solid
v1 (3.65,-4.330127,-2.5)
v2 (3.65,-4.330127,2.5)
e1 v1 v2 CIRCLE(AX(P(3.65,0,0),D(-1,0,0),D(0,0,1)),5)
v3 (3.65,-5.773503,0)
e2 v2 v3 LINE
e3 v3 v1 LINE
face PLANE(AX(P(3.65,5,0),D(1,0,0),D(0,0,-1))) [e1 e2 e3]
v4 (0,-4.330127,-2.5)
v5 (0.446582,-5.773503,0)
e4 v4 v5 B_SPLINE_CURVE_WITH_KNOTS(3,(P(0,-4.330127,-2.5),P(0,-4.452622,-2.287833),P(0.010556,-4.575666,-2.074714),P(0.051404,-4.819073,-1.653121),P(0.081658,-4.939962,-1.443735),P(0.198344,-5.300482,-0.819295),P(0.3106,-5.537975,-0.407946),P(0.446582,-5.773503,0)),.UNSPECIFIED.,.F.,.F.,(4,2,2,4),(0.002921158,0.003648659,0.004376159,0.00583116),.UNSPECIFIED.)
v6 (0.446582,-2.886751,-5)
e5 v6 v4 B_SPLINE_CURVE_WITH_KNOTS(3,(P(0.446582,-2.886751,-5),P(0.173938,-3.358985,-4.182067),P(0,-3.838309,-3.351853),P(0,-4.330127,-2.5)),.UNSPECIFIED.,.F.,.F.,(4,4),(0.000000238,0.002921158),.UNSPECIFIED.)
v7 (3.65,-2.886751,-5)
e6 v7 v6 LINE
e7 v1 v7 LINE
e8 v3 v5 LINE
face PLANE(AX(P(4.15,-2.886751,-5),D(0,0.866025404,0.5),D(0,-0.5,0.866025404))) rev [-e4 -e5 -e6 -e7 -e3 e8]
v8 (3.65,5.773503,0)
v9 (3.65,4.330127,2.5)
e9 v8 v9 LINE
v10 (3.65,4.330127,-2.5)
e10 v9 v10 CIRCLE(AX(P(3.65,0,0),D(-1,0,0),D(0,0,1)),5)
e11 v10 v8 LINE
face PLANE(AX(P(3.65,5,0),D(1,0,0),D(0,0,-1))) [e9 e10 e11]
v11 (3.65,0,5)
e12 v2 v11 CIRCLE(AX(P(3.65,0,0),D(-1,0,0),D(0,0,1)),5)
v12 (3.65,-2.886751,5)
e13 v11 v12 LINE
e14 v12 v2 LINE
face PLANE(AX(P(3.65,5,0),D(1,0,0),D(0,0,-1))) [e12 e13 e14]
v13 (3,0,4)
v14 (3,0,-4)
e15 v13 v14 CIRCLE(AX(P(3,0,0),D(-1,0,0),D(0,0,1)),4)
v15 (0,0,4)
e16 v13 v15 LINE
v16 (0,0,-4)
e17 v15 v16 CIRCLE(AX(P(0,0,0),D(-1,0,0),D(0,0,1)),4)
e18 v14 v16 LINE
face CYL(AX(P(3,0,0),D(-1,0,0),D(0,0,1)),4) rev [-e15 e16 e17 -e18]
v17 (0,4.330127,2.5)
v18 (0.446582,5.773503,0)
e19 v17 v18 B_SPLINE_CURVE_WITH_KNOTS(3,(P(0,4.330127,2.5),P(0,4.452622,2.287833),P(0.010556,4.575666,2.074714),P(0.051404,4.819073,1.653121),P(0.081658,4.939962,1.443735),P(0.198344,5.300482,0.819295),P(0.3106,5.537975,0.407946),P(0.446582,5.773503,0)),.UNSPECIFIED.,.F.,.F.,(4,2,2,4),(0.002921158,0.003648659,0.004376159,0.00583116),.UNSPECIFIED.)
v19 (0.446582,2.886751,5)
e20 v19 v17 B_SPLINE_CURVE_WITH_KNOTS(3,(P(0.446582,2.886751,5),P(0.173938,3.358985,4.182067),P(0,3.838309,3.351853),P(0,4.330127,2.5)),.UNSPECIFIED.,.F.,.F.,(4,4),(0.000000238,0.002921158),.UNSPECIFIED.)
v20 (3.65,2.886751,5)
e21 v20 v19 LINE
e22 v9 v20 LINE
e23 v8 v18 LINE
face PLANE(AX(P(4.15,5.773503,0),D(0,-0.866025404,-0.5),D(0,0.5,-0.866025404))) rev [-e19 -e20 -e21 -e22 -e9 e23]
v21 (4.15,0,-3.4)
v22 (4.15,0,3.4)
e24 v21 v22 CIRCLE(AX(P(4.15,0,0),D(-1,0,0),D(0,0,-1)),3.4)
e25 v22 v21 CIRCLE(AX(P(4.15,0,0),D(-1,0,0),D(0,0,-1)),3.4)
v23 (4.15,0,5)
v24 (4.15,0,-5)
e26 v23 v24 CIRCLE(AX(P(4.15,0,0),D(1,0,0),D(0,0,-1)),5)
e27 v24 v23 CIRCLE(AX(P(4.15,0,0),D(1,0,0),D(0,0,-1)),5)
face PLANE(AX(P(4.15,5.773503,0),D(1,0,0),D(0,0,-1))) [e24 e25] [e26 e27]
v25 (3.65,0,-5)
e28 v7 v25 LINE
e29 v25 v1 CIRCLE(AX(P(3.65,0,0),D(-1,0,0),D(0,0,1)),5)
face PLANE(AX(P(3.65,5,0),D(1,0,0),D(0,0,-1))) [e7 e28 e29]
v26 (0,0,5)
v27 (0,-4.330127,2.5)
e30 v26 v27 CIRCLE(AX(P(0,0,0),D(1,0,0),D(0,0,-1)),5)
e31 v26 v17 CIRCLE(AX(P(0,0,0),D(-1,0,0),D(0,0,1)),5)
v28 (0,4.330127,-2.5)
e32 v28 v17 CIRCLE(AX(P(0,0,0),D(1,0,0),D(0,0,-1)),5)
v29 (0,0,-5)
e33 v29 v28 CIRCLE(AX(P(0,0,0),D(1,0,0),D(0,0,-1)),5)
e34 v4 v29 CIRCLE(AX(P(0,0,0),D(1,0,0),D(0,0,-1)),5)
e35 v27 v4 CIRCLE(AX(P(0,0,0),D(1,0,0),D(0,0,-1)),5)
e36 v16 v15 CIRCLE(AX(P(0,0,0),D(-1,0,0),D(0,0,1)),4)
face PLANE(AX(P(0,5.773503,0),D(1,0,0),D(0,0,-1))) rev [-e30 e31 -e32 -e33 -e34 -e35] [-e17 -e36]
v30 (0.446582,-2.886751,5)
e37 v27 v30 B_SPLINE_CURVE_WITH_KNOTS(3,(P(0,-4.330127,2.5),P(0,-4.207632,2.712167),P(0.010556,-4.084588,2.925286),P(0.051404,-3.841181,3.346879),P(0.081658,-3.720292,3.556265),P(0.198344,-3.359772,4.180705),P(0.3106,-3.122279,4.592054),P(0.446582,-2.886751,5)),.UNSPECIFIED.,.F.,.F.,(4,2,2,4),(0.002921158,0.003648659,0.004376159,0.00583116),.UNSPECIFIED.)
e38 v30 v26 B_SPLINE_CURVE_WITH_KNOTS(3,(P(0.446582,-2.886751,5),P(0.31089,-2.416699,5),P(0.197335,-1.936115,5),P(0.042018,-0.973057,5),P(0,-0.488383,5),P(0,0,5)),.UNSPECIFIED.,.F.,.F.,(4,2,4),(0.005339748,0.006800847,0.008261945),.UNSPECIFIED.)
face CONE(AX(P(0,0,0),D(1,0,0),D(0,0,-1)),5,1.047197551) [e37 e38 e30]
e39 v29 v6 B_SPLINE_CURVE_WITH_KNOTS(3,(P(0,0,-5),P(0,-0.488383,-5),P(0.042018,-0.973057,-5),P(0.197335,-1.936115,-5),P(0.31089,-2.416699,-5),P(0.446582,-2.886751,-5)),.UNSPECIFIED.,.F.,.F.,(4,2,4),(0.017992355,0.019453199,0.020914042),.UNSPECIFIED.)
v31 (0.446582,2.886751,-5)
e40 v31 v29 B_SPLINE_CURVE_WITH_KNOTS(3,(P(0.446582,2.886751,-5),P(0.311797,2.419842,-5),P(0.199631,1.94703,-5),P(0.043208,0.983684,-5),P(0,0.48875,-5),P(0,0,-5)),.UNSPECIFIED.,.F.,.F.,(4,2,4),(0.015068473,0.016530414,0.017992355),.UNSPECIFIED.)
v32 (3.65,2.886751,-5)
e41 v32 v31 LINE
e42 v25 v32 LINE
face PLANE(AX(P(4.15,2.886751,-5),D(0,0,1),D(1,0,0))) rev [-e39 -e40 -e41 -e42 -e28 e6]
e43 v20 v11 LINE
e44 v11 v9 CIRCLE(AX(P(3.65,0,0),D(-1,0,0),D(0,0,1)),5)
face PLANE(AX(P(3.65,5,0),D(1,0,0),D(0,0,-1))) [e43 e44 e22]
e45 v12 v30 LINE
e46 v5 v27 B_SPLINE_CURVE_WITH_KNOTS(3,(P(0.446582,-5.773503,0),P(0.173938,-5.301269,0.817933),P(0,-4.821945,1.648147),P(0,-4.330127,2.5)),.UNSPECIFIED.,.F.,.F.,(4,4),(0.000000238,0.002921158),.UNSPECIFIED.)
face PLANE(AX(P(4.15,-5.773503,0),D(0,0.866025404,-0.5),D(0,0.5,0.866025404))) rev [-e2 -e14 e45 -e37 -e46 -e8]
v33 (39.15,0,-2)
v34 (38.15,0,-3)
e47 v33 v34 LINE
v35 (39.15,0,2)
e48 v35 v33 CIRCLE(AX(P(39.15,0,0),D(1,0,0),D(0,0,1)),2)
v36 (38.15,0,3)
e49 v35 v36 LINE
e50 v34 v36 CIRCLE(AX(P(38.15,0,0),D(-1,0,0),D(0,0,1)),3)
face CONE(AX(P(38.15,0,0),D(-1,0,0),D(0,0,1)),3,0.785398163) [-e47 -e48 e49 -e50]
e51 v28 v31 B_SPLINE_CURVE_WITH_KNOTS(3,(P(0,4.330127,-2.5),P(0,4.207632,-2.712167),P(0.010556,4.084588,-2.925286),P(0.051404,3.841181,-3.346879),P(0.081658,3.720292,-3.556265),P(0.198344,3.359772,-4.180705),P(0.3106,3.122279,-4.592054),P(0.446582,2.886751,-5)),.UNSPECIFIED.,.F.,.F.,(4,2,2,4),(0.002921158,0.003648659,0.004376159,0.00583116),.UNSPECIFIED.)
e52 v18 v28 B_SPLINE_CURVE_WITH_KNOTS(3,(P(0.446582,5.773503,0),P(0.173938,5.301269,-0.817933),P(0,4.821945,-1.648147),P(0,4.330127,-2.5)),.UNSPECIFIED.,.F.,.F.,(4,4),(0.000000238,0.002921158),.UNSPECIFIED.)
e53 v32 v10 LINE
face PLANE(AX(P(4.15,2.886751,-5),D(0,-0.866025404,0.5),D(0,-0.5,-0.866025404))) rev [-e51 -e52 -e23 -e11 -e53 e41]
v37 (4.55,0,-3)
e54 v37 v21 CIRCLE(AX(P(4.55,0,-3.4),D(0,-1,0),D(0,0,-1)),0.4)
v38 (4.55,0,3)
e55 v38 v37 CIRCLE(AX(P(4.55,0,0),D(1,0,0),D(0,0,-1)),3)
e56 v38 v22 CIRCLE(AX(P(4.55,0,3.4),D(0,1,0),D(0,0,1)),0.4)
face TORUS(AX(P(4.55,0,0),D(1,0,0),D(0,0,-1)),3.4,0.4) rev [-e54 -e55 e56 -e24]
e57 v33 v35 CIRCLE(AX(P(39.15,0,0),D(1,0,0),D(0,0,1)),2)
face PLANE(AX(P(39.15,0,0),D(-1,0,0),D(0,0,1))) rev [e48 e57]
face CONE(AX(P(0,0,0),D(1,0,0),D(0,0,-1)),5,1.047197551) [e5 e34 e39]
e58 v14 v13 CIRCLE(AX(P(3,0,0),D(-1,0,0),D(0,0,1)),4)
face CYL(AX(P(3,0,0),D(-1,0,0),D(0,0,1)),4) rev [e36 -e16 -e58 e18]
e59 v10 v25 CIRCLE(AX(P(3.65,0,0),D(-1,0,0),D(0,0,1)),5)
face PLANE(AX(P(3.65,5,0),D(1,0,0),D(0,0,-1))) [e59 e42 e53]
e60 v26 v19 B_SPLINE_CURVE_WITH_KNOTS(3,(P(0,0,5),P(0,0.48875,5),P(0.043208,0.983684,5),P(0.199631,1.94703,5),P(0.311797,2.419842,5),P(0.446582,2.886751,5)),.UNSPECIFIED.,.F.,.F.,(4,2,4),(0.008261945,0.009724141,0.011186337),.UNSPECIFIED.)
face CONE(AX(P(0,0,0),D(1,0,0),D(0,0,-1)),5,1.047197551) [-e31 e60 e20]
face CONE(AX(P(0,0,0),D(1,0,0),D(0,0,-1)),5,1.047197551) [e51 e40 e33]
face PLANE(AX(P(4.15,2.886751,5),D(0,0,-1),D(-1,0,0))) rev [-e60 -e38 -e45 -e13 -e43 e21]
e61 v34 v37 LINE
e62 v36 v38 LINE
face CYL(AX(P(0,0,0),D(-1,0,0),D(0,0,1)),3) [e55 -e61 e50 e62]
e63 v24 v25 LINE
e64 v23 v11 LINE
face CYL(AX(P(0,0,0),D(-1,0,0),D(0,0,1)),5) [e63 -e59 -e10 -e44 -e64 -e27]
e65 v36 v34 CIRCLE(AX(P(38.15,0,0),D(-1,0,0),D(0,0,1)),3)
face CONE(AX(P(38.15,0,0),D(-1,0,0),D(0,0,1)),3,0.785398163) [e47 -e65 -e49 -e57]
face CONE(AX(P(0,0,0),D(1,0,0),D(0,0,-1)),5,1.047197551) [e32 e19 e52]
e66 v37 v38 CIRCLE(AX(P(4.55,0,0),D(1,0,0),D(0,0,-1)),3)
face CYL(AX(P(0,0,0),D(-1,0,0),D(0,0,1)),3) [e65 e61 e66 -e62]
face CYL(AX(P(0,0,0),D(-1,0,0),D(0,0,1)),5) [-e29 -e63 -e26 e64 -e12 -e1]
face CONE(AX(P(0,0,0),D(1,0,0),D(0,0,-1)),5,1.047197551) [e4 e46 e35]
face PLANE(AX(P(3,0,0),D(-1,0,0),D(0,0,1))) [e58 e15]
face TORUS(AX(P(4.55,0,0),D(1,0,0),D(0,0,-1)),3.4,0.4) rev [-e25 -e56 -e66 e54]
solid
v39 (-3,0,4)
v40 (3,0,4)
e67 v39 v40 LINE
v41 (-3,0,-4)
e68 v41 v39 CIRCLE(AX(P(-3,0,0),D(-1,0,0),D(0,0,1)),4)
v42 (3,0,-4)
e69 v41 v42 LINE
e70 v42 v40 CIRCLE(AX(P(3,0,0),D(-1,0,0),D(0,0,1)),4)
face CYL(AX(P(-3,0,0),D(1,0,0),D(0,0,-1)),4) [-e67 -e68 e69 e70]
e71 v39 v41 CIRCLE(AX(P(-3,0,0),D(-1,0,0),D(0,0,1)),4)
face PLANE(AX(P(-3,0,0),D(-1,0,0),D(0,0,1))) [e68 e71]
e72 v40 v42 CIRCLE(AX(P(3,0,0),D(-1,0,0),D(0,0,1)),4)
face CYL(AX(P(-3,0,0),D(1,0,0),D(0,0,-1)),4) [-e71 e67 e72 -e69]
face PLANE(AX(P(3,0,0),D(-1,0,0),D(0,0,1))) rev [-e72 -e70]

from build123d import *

# Parameters (mm, degrees)
EXTRUDE_371_DEPTH   = 4.15
SKETCH_4_W          = 0.5
SKETCH_4_H          = 10.773502692
CHAMFER_1937_SIZE   = 1
FILLET_1988_R       = 0.4
SKETCH_7_R          = 4
CUT_EXTRUDE_1_DEPTH = 3
SKETCH_8_R          = 4
EXTRUDE_1_DEPTH     = 6


with BuildPart() as part:
    # 草图1 → Extrude 371 (new body)
    with BuildSketch(Plane(origin=(0, 0, 0), x_dir=(0, 0, -1), z_dir=(1, 0, 0))):
        Polygon((5, 2.886751346), (5, -2.886751346), (0, -5.773502692), (-5, -2.886751346), (-5, 2.886751346), (0, 5.773502692), align=None)
    extrude(amount=EXTRUDE_371_DEPTH)

    # 草图2 → 凸台-旋转1 (revolve)
    with BuildSketch(Plane.XY, mode=Mode.PRIVATE) as revolve_1_sk:
        Polygon((0, 0), (39.15, 0), (39.15, 1.9175), (39.15, 3), (0, 3), align=None)
    revolve(revolve_1_sk.sketch.rotate(Axis((0, 0, 0), (1, 0, 0)), 90), axis=Axis((0, 0, 0), (1, 0, 0)))

    # 草图3 → 切除-旋转1 (revolve, cut)
    with BuildSketch(Plane.XY):
        Polygon((0, 5), (3.333333333, 10.773502692), (3.333333333, 15.773502692), (-10, 15.773502692), (-10, 5), align=None)
    revolve(axis=Axis((0, 0, 0), (1, 0, 0)), mode=Mode.SUBTRACT)

    # 草图5 → 切除-旋转2 (revolve, cut)
    with BuildSketch(Plane.XY):
        Polygon((4.15, 5), (0.816666667, 10.773502692), (0.816666667, 15.773502692), (10.816666667, 15.773502692), (10.816666667, 5), align=None)
    revolve(axis=Axis((0, 0, 0), (1, 0, 0)), mode=Mode.SUBTRACT)

    # 草图4 → 切除-旋转3 (revolve, cut)
    with BuildSketch(Plane.XY, mode=Mode.PRIVATE) as cut_revolve_3_sk:
        with Locations((3.9, 10.386751346)):
            Rectangle(SKETCH_4_W, SKETCH_4_H)
    revolve(cut_revolve_3_sk.sketch.rotate(Axis((0, 0, 0), (1, 0, 0)), 270), axis=Axis((0, 0, 0), (1, 0, 0)), mode=Mode.SUBTRACT)

    # Chamfer 1937
    chamfer_1937_edges = [part.edges().sort_by_distance(p)[0] for p in [
        (39.15, 0, -3),
    ]]
    chamfer(chamfer_1937_edges, length=CHAMFER_1937_SIZE)

    # Fillet 1988
    fillet_1988_edges = [part.edges().sort_by_distance(p)[0] for p in [
        (4.15, 0, -3),
    ]]
    fillet(fillet_1988_edges, radius=FILLET_1988_R)

    # 草图7 → 切除-拉伸1 (cut)
    with BuildSketch(Plane.ZY):
        Circle(SKETCH_7_R)
    extrude(amount=-CUT_EXTRUDE_1_DEPTH, mode=Mode.SUBTRACT)


with BuildPart() as body_2:
    # 草图8 → 凸台-拉伸1 (new body)
    with BuildSketch(Plane.ZY.offset(-3)):
        Circle(SKETCH_8_R)
    extrude(amount=EXTRUDE_1_DEPTH)


solid = Compound([part.part, body_2.part])
